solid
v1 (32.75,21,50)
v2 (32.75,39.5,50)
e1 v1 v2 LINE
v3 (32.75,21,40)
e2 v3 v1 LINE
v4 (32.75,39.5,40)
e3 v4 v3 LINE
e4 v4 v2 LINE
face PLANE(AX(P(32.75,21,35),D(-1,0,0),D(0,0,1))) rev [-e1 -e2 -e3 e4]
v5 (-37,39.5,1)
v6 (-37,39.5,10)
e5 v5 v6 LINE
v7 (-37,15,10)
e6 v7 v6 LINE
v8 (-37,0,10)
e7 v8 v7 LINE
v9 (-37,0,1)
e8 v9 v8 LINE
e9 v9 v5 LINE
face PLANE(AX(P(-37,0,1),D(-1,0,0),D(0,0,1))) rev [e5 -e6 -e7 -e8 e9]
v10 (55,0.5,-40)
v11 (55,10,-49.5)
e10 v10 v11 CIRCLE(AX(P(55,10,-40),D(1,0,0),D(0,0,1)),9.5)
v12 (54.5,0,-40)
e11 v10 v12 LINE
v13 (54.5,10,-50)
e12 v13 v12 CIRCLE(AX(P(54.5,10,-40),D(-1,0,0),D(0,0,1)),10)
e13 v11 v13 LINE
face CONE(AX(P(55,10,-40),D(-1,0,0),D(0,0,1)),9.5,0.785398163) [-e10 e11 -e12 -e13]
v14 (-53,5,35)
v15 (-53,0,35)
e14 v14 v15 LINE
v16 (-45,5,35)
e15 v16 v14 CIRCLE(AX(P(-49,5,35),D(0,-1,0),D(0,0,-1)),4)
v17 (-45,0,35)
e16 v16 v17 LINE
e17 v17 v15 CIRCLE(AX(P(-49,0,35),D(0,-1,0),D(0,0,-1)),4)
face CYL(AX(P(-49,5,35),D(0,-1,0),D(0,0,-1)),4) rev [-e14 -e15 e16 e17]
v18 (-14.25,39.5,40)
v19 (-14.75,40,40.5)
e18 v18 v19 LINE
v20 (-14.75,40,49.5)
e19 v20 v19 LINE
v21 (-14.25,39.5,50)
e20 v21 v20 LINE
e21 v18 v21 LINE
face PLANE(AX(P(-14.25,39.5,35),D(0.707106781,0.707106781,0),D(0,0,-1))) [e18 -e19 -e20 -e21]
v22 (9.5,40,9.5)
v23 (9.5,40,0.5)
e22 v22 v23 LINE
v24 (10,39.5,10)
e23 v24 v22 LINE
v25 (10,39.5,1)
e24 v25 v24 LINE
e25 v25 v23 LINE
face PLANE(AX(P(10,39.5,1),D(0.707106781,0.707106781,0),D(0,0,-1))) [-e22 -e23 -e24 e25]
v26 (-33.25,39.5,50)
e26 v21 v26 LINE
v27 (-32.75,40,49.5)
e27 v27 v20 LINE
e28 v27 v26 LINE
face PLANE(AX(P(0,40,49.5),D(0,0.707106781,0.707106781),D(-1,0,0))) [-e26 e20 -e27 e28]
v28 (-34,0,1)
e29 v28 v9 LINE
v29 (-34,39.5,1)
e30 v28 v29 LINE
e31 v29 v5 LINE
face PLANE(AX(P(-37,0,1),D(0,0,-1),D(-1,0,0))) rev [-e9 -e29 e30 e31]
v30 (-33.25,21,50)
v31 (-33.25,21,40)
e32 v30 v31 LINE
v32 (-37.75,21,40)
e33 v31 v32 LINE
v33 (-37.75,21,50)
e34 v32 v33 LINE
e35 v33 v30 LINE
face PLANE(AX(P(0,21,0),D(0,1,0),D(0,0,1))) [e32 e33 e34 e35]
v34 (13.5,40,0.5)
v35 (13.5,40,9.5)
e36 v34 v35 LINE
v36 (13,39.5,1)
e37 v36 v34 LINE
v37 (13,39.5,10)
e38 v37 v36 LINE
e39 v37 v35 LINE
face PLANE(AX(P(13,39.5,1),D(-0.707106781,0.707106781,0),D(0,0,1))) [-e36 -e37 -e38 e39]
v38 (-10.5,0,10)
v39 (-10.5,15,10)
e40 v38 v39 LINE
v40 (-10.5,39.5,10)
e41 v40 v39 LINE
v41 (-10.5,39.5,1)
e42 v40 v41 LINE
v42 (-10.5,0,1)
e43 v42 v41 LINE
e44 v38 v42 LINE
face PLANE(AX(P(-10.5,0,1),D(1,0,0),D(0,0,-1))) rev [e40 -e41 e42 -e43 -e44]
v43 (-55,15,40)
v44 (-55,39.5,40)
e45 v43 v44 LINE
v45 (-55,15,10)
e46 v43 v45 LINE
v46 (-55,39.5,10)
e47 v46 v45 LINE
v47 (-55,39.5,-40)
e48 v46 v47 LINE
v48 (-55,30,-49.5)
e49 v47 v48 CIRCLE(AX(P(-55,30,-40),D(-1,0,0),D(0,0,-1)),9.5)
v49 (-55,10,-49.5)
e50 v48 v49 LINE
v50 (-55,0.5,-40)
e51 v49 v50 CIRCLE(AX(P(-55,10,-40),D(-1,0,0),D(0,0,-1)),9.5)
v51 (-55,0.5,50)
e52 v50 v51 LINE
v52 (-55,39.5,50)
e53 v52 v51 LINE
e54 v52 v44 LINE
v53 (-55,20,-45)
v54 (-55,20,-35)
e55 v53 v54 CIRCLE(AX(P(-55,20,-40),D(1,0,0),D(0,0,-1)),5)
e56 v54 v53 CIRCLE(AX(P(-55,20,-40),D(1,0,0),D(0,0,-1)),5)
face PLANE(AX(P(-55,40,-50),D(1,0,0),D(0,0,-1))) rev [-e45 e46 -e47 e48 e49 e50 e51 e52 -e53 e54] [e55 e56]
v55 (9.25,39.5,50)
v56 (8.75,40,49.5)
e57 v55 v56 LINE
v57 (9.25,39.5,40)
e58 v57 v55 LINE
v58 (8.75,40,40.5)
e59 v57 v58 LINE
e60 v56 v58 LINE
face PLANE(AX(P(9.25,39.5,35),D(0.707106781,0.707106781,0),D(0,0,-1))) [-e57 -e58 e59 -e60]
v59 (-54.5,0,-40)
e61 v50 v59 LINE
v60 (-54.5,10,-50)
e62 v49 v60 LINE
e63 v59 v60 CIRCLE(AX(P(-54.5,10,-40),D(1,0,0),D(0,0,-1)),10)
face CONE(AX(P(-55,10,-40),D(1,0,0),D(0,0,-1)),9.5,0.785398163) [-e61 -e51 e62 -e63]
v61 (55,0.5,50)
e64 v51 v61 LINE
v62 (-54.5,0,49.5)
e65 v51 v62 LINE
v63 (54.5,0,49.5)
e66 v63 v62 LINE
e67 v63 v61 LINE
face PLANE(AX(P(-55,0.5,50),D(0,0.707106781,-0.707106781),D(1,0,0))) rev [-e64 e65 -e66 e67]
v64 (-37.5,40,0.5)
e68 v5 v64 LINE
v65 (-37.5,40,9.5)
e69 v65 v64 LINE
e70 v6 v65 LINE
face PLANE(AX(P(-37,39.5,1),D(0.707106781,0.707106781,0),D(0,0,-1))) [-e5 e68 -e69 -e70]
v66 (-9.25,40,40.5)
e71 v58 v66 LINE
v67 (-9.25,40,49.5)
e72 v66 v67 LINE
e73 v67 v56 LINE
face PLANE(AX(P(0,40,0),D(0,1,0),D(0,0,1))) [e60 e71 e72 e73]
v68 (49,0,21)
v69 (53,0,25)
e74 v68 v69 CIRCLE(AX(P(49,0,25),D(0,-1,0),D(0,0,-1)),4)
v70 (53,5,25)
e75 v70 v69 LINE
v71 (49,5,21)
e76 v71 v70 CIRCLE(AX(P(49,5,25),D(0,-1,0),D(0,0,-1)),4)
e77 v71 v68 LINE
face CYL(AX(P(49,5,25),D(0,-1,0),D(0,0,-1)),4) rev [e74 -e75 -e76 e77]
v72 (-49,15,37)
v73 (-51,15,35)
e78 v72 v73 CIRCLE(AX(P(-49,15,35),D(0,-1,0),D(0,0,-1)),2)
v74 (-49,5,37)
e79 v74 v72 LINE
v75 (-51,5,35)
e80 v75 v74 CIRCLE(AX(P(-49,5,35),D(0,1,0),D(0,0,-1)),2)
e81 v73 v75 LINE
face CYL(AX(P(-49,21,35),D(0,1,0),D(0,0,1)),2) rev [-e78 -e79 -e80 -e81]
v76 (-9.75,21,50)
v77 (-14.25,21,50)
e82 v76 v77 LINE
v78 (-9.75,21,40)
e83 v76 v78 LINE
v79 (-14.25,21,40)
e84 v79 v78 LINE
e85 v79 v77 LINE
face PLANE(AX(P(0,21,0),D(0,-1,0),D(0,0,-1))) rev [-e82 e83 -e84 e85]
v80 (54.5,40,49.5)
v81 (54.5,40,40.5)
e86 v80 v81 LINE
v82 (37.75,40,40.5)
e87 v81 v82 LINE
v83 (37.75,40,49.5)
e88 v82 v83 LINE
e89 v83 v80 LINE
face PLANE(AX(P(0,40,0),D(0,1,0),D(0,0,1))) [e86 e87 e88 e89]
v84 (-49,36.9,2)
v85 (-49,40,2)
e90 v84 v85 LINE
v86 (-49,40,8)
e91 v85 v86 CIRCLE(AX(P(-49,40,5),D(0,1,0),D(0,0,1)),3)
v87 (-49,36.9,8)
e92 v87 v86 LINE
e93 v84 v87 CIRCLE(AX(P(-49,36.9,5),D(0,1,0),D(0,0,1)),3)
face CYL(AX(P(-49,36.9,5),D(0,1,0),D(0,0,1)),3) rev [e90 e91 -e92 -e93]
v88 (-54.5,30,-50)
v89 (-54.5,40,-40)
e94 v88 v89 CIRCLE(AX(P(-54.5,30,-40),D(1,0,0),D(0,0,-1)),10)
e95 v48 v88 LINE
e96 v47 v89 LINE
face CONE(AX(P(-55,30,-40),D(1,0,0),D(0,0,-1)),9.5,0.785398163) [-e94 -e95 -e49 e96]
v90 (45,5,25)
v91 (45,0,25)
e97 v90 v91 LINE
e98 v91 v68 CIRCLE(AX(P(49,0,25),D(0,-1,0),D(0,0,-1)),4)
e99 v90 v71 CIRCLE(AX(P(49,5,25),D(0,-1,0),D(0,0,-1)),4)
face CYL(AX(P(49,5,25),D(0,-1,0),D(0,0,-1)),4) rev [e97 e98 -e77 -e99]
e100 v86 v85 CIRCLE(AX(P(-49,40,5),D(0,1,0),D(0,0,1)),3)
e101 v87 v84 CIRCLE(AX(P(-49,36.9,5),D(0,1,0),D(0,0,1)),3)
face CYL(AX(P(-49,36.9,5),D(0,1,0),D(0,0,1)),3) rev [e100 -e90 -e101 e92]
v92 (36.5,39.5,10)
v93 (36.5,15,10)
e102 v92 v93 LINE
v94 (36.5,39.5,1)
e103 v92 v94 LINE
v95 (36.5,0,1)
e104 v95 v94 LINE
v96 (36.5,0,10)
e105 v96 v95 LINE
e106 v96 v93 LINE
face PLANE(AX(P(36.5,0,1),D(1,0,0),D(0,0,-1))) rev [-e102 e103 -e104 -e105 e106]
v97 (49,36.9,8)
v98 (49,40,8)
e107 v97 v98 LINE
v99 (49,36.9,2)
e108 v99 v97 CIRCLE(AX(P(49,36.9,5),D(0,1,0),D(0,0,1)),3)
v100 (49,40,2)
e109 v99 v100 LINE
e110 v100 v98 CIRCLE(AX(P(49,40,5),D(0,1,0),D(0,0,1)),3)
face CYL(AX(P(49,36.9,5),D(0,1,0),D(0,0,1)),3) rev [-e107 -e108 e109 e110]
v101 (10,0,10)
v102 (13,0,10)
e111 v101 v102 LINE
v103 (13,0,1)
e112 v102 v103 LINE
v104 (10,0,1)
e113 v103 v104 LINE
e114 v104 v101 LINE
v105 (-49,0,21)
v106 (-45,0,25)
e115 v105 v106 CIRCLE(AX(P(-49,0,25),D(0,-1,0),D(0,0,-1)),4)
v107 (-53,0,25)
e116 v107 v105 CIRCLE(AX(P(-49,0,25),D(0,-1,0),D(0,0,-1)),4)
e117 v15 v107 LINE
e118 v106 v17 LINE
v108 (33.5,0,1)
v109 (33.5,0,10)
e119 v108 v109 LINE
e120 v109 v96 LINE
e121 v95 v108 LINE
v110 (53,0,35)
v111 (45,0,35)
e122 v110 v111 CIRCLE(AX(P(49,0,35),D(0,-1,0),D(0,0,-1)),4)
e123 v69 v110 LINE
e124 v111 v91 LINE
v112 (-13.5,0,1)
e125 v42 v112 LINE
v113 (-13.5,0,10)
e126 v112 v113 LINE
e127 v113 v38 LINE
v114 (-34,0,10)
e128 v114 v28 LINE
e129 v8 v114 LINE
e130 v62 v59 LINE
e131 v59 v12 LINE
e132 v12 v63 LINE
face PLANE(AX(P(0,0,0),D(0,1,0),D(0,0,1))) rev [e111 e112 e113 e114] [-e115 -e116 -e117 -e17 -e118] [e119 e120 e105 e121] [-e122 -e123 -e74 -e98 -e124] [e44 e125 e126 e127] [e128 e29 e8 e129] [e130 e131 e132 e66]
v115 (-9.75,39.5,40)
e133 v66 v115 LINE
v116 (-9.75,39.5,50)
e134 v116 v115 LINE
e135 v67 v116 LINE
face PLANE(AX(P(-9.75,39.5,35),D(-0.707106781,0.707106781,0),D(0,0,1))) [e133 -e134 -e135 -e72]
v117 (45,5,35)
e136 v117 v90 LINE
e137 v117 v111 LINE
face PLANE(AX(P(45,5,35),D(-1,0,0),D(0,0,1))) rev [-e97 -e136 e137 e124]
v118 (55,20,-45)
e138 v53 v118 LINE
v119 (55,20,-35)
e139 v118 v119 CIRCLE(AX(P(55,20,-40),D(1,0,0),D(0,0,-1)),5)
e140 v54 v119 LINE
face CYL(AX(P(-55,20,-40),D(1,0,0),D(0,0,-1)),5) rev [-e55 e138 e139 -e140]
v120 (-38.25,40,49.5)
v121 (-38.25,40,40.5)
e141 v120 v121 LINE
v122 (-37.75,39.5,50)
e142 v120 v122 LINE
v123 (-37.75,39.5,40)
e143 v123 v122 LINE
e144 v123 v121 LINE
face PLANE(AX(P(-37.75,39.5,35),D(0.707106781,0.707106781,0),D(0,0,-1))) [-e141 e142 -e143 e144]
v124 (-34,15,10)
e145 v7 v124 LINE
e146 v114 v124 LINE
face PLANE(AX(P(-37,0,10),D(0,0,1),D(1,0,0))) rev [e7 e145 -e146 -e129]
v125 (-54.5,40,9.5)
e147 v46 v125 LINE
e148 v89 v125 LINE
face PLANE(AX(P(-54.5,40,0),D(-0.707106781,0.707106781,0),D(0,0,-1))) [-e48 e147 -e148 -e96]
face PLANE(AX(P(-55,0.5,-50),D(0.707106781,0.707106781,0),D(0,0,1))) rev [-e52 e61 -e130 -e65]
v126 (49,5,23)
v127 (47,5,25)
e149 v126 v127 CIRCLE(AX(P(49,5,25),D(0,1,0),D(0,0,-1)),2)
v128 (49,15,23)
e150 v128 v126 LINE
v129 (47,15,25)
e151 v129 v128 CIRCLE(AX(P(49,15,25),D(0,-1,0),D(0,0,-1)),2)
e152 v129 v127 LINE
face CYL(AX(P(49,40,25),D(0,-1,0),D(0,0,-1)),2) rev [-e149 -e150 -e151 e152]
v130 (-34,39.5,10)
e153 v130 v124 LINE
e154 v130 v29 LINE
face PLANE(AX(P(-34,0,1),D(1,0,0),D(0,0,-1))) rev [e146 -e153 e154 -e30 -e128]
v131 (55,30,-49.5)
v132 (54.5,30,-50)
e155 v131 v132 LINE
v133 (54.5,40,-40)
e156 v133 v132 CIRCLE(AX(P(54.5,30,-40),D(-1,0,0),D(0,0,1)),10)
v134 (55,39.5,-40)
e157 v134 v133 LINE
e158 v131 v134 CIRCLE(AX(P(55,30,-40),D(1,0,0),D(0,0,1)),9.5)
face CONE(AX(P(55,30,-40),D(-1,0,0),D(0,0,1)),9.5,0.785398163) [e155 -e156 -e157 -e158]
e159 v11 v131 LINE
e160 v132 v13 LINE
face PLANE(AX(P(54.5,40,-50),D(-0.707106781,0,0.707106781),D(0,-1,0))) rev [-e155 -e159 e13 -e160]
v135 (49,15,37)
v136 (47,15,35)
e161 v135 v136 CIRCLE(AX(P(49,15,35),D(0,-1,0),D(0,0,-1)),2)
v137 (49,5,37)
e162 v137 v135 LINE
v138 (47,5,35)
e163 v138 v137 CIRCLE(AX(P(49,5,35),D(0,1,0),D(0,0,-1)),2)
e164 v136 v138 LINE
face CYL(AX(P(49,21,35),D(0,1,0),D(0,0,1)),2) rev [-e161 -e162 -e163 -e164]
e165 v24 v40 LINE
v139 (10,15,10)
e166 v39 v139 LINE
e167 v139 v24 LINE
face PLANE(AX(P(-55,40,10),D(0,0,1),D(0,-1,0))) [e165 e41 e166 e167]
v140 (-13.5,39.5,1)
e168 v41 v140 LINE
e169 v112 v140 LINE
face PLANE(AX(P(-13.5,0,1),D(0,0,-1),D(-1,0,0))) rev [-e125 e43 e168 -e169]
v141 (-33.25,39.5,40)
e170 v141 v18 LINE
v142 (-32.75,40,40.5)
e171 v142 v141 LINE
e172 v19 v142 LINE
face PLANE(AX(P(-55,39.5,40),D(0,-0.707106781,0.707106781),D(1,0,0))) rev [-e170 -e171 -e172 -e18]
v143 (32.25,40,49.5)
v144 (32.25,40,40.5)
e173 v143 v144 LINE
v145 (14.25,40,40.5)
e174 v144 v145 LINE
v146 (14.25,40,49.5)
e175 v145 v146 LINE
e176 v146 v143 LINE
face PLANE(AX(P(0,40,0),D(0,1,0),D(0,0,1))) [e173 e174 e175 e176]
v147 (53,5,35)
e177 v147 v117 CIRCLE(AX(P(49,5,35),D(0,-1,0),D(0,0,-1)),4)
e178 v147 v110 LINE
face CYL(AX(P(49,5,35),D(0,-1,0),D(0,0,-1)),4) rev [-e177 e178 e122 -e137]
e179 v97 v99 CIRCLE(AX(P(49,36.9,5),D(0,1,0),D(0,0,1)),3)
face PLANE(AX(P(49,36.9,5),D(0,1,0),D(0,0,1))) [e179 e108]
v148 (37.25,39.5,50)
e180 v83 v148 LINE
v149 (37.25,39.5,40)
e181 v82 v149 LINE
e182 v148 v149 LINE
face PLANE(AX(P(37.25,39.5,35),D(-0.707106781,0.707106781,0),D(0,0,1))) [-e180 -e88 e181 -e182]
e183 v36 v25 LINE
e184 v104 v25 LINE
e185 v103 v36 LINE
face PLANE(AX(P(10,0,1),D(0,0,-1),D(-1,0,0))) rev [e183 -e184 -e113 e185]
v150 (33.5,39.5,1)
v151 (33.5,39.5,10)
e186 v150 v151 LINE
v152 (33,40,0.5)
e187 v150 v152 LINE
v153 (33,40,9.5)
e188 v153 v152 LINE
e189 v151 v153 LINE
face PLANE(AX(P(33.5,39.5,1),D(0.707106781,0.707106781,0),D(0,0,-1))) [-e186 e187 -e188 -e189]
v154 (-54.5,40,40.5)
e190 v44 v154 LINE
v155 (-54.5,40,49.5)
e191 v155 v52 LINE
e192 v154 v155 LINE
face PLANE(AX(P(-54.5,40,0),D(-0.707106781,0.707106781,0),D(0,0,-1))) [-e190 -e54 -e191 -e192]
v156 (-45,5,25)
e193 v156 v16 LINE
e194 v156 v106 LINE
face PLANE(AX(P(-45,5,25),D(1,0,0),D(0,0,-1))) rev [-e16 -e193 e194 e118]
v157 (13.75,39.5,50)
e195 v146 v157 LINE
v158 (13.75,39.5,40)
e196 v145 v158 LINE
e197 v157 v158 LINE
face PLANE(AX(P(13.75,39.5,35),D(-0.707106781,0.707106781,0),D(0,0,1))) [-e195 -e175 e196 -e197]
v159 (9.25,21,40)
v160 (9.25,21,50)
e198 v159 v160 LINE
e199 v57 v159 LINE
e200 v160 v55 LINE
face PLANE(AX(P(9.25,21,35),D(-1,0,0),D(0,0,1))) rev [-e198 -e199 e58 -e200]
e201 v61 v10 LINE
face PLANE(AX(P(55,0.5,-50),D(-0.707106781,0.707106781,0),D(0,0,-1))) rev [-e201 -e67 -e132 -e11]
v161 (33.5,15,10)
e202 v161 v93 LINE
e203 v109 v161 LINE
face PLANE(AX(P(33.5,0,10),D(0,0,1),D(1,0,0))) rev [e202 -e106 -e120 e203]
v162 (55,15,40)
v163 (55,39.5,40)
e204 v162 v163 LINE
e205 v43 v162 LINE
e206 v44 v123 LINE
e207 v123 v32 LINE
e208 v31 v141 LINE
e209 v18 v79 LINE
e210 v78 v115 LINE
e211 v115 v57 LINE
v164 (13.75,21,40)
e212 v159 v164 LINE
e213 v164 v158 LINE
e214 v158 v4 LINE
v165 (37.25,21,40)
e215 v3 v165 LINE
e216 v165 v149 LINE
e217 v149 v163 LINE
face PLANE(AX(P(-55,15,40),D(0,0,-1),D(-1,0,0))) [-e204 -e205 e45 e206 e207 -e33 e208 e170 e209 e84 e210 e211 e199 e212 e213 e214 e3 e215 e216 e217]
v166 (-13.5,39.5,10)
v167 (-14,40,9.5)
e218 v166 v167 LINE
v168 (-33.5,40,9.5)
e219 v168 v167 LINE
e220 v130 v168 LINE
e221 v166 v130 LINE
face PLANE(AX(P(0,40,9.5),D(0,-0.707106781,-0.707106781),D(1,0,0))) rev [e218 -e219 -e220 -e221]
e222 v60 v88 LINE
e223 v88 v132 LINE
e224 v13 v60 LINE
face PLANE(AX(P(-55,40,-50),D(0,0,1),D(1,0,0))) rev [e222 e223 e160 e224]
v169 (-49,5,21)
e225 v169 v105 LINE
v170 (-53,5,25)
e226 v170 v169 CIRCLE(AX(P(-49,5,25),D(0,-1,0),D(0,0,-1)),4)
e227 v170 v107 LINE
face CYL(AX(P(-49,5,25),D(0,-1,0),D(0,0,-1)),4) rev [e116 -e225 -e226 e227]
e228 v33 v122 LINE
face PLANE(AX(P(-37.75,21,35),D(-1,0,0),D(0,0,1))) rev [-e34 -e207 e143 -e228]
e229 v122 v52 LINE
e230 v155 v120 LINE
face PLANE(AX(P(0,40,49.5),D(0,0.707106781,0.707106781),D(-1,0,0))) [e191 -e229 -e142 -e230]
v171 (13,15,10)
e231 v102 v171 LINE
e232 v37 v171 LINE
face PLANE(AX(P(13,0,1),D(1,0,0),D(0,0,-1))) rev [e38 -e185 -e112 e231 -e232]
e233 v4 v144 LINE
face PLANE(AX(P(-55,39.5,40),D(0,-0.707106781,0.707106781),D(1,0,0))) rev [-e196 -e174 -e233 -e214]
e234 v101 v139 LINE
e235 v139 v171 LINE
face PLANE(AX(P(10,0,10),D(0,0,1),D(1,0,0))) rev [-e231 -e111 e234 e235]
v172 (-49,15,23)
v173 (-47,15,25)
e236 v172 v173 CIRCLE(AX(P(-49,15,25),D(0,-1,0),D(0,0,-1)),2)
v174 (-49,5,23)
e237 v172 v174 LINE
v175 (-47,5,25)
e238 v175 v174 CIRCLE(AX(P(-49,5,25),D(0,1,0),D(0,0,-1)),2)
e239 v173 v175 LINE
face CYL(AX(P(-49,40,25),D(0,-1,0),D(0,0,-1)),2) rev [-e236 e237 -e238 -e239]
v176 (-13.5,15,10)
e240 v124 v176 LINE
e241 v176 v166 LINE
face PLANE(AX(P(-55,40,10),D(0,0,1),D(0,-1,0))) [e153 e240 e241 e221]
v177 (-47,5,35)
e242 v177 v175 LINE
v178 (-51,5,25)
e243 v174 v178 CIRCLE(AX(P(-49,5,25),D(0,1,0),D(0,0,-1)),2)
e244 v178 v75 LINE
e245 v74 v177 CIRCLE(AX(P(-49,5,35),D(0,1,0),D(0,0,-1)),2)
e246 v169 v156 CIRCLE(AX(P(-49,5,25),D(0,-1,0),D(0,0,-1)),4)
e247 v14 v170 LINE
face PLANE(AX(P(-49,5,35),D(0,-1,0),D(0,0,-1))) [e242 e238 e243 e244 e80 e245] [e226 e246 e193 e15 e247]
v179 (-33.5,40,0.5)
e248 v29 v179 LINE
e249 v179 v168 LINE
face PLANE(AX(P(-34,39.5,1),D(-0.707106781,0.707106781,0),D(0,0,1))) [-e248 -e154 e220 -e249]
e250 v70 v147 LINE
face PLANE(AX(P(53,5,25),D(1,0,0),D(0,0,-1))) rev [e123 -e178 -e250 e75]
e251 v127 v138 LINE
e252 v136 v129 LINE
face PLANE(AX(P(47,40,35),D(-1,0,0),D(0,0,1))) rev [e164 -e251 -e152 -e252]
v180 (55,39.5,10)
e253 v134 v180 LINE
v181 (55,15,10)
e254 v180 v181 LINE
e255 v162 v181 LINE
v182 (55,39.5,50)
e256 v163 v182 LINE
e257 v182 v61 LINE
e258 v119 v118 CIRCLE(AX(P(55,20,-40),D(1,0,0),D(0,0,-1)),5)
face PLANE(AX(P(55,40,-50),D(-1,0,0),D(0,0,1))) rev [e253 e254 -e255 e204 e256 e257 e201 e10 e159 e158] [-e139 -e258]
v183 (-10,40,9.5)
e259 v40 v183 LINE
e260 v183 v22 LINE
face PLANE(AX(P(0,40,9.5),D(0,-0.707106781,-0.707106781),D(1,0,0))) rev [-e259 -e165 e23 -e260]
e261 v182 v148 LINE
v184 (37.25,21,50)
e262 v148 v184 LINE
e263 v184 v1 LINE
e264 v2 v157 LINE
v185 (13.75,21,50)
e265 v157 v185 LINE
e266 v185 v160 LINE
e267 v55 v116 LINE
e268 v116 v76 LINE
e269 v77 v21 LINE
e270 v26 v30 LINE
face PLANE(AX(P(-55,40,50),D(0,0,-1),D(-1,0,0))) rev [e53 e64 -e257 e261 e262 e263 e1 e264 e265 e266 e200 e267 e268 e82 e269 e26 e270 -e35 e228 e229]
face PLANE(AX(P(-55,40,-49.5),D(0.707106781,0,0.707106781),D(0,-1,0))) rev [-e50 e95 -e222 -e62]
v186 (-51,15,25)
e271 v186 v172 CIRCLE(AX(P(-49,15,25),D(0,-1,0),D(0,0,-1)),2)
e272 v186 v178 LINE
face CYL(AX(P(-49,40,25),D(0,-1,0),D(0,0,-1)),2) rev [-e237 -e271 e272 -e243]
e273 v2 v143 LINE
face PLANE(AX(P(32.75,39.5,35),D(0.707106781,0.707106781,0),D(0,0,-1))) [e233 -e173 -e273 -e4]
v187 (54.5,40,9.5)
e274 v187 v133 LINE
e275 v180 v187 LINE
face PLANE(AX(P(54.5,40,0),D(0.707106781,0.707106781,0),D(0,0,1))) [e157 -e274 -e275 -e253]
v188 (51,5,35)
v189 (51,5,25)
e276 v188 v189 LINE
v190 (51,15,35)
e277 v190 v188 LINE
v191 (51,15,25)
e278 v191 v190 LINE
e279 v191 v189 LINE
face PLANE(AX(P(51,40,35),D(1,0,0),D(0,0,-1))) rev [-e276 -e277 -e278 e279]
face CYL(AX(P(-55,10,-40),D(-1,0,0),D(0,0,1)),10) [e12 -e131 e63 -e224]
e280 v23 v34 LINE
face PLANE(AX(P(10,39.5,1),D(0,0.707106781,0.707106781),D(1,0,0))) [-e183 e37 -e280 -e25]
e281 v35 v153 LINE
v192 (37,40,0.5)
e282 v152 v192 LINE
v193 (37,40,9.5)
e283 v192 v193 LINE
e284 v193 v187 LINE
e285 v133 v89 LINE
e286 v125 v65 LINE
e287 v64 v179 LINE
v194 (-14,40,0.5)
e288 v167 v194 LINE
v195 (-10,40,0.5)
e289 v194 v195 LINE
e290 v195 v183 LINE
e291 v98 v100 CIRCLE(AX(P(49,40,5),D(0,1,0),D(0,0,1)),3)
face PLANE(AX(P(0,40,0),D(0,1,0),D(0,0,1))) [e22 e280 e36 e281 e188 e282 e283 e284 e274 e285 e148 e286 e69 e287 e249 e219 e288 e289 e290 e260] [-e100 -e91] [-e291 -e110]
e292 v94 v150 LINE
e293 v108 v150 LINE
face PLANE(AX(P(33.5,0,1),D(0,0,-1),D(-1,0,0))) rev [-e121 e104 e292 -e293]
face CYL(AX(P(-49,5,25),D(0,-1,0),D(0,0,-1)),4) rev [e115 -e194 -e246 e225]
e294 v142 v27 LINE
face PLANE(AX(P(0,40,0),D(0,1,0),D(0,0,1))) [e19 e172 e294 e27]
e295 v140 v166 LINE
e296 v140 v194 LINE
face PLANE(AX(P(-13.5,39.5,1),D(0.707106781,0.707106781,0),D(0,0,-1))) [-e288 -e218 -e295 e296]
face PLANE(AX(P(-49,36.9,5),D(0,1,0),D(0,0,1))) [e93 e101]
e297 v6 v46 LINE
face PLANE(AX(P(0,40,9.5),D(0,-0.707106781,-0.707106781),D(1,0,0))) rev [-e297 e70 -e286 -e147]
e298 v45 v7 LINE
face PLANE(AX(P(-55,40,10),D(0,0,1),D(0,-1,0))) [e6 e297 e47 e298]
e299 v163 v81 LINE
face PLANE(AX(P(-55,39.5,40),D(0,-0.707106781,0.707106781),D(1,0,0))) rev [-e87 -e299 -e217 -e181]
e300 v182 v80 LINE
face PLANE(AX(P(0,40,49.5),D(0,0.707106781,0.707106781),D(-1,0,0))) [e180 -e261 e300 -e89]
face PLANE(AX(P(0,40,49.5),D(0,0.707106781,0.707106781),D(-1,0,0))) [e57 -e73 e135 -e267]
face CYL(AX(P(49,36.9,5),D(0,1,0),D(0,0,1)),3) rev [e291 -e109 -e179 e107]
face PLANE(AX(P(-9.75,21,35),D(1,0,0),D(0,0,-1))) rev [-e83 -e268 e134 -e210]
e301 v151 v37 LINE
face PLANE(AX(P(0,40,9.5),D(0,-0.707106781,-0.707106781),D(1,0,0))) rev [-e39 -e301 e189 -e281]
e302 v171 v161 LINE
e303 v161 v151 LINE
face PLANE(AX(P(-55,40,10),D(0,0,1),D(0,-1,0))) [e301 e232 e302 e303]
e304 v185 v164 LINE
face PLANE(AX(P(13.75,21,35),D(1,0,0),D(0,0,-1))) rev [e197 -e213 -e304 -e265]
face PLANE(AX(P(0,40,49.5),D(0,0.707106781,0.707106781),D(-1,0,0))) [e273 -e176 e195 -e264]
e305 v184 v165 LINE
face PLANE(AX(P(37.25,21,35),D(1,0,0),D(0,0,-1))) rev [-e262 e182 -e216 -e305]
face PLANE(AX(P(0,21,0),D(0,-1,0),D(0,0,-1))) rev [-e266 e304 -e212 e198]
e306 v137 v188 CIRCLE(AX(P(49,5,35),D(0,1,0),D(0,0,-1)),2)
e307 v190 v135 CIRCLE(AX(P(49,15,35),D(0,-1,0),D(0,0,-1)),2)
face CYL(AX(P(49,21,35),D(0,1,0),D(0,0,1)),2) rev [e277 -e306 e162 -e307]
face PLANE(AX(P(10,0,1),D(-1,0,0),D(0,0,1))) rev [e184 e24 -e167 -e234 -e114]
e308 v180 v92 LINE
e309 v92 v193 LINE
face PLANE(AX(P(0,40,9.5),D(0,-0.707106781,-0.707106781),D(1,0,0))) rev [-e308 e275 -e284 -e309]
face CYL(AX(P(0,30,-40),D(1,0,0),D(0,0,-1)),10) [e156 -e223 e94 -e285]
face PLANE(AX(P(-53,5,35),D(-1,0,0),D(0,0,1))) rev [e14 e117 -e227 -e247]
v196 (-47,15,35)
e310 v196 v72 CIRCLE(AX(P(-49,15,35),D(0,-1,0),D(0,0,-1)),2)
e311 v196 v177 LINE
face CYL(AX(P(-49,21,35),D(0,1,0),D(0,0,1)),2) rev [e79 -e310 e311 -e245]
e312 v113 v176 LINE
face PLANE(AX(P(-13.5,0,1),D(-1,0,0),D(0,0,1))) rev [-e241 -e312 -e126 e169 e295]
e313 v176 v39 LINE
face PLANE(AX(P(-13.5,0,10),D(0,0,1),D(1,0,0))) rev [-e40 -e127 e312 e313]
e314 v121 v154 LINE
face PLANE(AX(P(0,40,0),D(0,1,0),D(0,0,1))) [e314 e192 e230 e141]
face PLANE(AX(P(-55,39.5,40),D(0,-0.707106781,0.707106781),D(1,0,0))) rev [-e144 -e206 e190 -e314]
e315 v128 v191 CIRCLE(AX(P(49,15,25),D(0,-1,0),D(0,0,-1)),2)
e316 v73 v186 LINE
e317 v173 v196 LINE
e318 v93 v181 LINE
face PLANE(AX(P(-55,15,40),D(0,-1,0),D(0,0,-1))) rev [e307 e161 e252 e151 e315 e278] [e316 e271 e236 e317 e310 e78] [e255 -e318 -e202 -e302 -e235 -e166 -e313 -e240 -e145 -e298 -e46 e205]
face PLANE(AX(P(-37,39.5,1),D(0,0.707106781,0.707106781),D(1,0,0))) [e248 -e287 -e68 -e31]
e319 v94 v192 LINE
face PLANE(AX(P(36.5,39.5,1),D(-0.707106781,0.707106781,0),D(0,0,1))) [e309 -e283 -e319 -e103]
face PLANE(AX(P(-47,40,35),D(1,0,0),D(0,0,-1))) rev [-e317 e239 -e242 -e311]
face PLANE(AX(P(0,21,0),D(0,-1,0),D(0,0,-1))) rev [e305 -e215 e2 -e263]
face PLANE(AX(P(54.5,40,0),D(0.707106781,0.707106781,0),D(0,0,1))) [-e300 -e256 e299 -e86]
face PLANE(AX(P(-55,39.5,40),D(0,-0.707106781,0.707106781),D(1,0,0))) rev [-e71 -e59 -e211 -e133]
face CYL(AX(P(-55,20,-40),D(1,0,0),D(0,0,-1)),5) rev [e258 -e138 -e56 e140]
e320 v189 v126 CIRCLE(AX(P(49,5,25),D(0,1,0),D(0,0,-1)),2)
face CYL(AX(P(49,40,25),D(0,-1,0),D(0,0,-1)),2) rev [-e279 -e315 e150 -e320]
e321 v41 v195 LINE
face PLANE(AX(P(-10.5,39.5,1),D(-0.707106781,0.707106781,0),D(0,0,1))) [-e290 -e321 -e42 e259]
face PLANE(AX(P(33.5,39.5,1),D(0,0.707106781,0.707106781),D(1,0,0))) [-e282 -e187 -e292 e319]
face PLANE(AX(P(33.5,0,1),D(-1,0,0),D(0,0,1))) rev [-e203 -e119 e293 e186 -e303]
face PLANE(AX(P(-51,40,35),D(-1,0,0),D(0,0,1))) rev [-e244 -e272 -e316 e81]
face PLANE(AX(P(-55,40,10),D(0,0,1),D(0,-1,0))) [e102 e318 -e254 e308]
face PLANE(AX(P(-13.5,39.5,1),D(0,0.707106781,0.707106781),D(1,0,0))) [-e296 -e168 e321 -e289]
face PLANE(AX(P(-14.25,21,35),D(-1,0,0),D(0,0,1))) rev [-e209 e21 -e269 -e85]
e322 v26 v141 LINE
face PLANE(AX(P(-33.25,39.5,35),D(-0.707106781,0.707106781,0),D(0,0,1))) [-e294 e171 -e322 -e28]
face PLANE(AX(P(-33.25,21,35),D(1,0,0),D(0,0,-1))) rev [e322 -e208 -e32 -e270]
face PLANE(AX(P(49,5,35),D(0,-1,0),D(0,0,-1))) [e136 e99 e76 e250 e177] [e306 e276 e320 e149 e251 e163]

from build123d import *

# Parameters (mm, degrees)
SKETCH7_W                = 110
SKETCH7_H                = 100
BOSS_EXTRUDE2_DEPTH      = 40
SKETCH8_W                = 3
SKETCH8_H                = 9
CUT_EXTRUDE1_DEPTH       = 85.409715081
SKETCH11_W               = 4.5
SKETCH11_H               = 17
CUT_EXTRUDE4_DEPTH       = 19
SKETCH9_W                = 30
SKETCH9_H                = 25
CUT_EXTRUDE5_DEPTH       = 128.279220614
SKETCH12_R               = 5
CUT_EXTRUDE6_DEPTH       = 128.279220614
F_4_0_4_DIAMETER_HOLE1_D = 4
CUT_EXTRUDE8_DEPTH       = 85.409715081
CUT_EXTRUDE9_DEPTH       = 5
FILLET1_R                = 10
CHAMFER1_SIZE            = 0.5
CHAMFER2_SIZE            = 0.5
CHAMFER3_SIZE            = 0.5
SKETCH20_R               = 3
CUT_EXTRUDE10_DEPTH      = 3.1


with BuildPart() as part:
    # Sketch7 → Boss-Extrude2 (new body)
    with BuildSketch(Plane(origin=(0, 0, 0), x_dir=(1, 0, 0), z_dir=(0, 1, 0))):
        Rectangle(SKETCH7_W, SKETCH7_H)
    extrude(amount=BOSS_EXTRUDE2_DEPTH)

    # Sketch8 → Cut-Extrude1 (cut, through all)
    with BuildSketch(Plane(origin=(0, 40, 0), x_dir=(1, 0, 0), z_dir=(0, 1, 0))):
        with Locations((-35.5, -5.5)):
            Rectangle(SKETCH8_W, SKETCH8_H)
        with Locations((-12, -5.5)):
            Rectangle(SKETCH8_W, SKETCH8_H)
        with Locations((11.5, -5.5)):
            Rectangle(SKETCH8_W, SKETCH8_H)
        with Locations((35, -5.5)):
            Rectangle(SKETCH8_W, SKETCH8_H)
    extrude(amount=-CUT_EXTRUDE1_DEPTH, mode=Mode.SUBTRACT)

    # Sketch11 → Cut-Extrude4 (cut)
    with BuildSketch(Plane(origin=(0, 40, 0), x_dir=(1, 0, 0), z_dir=(0, 1, 0))):
        with Locations((-35.5, -43.5)):
            Rectangle(SKETCH11_W, SKETCH11_H)
        with Locations((-12, -43.5)):
            Rectangle(SKETCH11_W, SKETCH11_H)
        with Locations((11.5, -43.5)):
            Rectangle(SKETCH11_W, SKETCH11_H)
        with Locations((35, -43.5)):
            Rectangle(SKETCH11_W, SKETCH11_H)
    extrude(amount=-CUT_EXTRUDE4_DEPTH, mode=Mode.SUBTRACT)

    # Sketch9 → Cut-Extrude5 (cut, through all)
    with BuildSketch(Plane(origin=(55, 0, 0), x_dir=(0, 0, -1), z_dir=(1, 0, 0))):
        with Locations((-25, 27.5)):
            Rectangle(SKETCH9_W, SKETCH9_H)
    extrude(amount=-CUT_EXTRUDE5_DEPTH, mode=Mode.SUBTRACT)

    # Sketch12 → Cut-Extrude6 (cut, through all)
    with BuildSketch(Plane(origin=(55, 0, 0), x_dir=(0, 0, -1), z_dir=(1, 0, 0))):
        with Locations((40, 20)):
            Circle(SKETCH12_R)
    extrude(amount=-CUT_EXTRUDE6_DEPTH, mode=Mode.SUBTRACT)

    # Ø4.0 (4) Diameter Hole1 (through all)
    with Locations(Plane(origin=(0, 21, 0), x_dir=(1, 0, 0), z_dir=(0, 1, 0))):
        with Locations((-49, -35), (49, -35)):
            Hole(F_4_0_4_DIAMETER_HOLE1_D / 2)

    # Sketch18 → Cut-Extrude8 (cut, through all)
    with BuildSketch(Plane.XZ):
        with BuildLine():
            Line((-47, 35), (-47, 25))
            ThreePointArc((-47, 25), (-49, 23), (-51, 25))
            Line((-51, 25), (-51, 35))
            ThreePointArc((-51, 35), (-49, 37), (-47, 35))
        make_face()
        with BuildLine():
            Line((47, 35), (47, 25))
            ThreePointArc((47, 25), (49, 23), (51, 25))
            Line((51, 25), (51, 35))
            ThreePointArc((51, 35), (49, 37), (47, 35))
        make_face()
    extrude(amount=-CUT_EXTRUDE8_DEPTH, mode=Mode.SUBTRACT)

    # Sketch19 → Cut-Extrude9 (cut)
    with BuildSketch(Plane.XZ):
        with BuildLine():
            Line((-53, 35), (-53, 25))
            ThreePointArc((-53, 25), (-49, 21), (-45, 25))
            Line((-45, 25), (-45, 35))
            ThreePointArc((-45, 35), (-49, 39), (-53, 35))
        make_face()
        with BuildLine():
            Line((45, 35), (45, 25))
            ThreePointArc((45, 25), (49, 21), (53, 25))
            Line((53, 25), (53, 35))
            ThreePointArc((53, 35), (49, 39), (45, 35))
        make_face()
    extrude(amount=-CUT_EXTRUDE9_DEPTH, mode=Mode.SUBTRACT)

    # Fillet1
    fillet1_edges = [part.edges().sort_by_distance(p)[0] for p in [
        (0, 0, -50),
        (0, 40, -50),
    ]]
    fillet(fillet1_edges, radius=FILLET1_R)

    # Chamfer1
    chamfer1_edges = [part.edges().sort_by_distance(p)[0] for p in [
        (0, 0, 50),
    ]]
    chamfer(chamfer1_edges, length=CHAMFER1_SIZE)

    # Chamfer2
    chamfer2_edges = [part.edges().sort_by_distance(p)[0] for p in [
        (-55, 0, 4.75),
        (55, 0, 4.75),
        (-55, 2.928932188, -47.071067812),
        (55, 2.928932188, -47.071067812),
        (-55, 20, -50),
        (55, 20, -50),
        (-55, 37.071067812, -47.071067812),
        (55, 37.071067812, -47.071067812),
        (-55, 40, -15),
        (-46, 40, 10),
        (-37, 40, 5.5),
        (-35.5, 40, 1),
        (-34, 40, 5.5),
        (-23.75, 40, 10),
        (-13.5, 40, 5.5),
        (-12, 40, 1),
        (-10.5, 40, 5.5),
        (-0.25, 40, 10),
        (10, 40, 5.5),
        (11.5, 40, 1),
        (13, 40, 5.5),
        (23.25, 40, 10),
        (33.5, 40, 5.5),
        (35, 40, 1),
        (36.5, 40, 5.5),
        (45.75, 40, 10),
        (55, 40, -15),
    ]]
    chamfer(chamfer2_edges, length=CHAMFER2_SIZE)

    # Chamfer3
    chamfer3_edges = [part.edges().sort_by_distance(p)[0] for p in [
        (-37.75, 40, 45),
        (-14.25, 40, 45),
        (9.25, 40, 45),
        (32.75, 40, 45),
        (-55, 40, 45),
        (-46.375, 40, 50),
        (46.125, 40, 40),
        (-46.375, 40, 40),
        (-23.75, 40, 40),
        (-0.25, 40, 40),
        (23.25, 40, 40),
        (55, 40, 45),
        (-23.75, 40, 50),
        (-0.25, 40, 50),
        (23.25, 40, 50),
        (46.125, 40, 50),
        (37.25, 40, 45),
        (13.75, 40, 45),
        (-9.75, 40, 45),
        (-33.25, 40, 45),
    ]]
    chamfer(chamfer3_edges, length=CHAMFER3_SIZE)

    # Sketch20 → Cut-Extrude10 (cut)
    with BuildSketch(Plane(origin=(0, 40, 0), x_dir=(1, 0, 0), z_dir=(0, 1, 0))):
        with Locations(Location((-49, -5, 0), (0, 0, 270))):
            Circle(SKETCH20_R)
        with Locations(Location((49, -5, 0), (0, 0, 270))):
            Circle(SKETCH20_R)
    extrude(amount=-CUT_EXTRUDE10_DEPTH, mode=Mode.SUBTRACT)


solid = part.part
